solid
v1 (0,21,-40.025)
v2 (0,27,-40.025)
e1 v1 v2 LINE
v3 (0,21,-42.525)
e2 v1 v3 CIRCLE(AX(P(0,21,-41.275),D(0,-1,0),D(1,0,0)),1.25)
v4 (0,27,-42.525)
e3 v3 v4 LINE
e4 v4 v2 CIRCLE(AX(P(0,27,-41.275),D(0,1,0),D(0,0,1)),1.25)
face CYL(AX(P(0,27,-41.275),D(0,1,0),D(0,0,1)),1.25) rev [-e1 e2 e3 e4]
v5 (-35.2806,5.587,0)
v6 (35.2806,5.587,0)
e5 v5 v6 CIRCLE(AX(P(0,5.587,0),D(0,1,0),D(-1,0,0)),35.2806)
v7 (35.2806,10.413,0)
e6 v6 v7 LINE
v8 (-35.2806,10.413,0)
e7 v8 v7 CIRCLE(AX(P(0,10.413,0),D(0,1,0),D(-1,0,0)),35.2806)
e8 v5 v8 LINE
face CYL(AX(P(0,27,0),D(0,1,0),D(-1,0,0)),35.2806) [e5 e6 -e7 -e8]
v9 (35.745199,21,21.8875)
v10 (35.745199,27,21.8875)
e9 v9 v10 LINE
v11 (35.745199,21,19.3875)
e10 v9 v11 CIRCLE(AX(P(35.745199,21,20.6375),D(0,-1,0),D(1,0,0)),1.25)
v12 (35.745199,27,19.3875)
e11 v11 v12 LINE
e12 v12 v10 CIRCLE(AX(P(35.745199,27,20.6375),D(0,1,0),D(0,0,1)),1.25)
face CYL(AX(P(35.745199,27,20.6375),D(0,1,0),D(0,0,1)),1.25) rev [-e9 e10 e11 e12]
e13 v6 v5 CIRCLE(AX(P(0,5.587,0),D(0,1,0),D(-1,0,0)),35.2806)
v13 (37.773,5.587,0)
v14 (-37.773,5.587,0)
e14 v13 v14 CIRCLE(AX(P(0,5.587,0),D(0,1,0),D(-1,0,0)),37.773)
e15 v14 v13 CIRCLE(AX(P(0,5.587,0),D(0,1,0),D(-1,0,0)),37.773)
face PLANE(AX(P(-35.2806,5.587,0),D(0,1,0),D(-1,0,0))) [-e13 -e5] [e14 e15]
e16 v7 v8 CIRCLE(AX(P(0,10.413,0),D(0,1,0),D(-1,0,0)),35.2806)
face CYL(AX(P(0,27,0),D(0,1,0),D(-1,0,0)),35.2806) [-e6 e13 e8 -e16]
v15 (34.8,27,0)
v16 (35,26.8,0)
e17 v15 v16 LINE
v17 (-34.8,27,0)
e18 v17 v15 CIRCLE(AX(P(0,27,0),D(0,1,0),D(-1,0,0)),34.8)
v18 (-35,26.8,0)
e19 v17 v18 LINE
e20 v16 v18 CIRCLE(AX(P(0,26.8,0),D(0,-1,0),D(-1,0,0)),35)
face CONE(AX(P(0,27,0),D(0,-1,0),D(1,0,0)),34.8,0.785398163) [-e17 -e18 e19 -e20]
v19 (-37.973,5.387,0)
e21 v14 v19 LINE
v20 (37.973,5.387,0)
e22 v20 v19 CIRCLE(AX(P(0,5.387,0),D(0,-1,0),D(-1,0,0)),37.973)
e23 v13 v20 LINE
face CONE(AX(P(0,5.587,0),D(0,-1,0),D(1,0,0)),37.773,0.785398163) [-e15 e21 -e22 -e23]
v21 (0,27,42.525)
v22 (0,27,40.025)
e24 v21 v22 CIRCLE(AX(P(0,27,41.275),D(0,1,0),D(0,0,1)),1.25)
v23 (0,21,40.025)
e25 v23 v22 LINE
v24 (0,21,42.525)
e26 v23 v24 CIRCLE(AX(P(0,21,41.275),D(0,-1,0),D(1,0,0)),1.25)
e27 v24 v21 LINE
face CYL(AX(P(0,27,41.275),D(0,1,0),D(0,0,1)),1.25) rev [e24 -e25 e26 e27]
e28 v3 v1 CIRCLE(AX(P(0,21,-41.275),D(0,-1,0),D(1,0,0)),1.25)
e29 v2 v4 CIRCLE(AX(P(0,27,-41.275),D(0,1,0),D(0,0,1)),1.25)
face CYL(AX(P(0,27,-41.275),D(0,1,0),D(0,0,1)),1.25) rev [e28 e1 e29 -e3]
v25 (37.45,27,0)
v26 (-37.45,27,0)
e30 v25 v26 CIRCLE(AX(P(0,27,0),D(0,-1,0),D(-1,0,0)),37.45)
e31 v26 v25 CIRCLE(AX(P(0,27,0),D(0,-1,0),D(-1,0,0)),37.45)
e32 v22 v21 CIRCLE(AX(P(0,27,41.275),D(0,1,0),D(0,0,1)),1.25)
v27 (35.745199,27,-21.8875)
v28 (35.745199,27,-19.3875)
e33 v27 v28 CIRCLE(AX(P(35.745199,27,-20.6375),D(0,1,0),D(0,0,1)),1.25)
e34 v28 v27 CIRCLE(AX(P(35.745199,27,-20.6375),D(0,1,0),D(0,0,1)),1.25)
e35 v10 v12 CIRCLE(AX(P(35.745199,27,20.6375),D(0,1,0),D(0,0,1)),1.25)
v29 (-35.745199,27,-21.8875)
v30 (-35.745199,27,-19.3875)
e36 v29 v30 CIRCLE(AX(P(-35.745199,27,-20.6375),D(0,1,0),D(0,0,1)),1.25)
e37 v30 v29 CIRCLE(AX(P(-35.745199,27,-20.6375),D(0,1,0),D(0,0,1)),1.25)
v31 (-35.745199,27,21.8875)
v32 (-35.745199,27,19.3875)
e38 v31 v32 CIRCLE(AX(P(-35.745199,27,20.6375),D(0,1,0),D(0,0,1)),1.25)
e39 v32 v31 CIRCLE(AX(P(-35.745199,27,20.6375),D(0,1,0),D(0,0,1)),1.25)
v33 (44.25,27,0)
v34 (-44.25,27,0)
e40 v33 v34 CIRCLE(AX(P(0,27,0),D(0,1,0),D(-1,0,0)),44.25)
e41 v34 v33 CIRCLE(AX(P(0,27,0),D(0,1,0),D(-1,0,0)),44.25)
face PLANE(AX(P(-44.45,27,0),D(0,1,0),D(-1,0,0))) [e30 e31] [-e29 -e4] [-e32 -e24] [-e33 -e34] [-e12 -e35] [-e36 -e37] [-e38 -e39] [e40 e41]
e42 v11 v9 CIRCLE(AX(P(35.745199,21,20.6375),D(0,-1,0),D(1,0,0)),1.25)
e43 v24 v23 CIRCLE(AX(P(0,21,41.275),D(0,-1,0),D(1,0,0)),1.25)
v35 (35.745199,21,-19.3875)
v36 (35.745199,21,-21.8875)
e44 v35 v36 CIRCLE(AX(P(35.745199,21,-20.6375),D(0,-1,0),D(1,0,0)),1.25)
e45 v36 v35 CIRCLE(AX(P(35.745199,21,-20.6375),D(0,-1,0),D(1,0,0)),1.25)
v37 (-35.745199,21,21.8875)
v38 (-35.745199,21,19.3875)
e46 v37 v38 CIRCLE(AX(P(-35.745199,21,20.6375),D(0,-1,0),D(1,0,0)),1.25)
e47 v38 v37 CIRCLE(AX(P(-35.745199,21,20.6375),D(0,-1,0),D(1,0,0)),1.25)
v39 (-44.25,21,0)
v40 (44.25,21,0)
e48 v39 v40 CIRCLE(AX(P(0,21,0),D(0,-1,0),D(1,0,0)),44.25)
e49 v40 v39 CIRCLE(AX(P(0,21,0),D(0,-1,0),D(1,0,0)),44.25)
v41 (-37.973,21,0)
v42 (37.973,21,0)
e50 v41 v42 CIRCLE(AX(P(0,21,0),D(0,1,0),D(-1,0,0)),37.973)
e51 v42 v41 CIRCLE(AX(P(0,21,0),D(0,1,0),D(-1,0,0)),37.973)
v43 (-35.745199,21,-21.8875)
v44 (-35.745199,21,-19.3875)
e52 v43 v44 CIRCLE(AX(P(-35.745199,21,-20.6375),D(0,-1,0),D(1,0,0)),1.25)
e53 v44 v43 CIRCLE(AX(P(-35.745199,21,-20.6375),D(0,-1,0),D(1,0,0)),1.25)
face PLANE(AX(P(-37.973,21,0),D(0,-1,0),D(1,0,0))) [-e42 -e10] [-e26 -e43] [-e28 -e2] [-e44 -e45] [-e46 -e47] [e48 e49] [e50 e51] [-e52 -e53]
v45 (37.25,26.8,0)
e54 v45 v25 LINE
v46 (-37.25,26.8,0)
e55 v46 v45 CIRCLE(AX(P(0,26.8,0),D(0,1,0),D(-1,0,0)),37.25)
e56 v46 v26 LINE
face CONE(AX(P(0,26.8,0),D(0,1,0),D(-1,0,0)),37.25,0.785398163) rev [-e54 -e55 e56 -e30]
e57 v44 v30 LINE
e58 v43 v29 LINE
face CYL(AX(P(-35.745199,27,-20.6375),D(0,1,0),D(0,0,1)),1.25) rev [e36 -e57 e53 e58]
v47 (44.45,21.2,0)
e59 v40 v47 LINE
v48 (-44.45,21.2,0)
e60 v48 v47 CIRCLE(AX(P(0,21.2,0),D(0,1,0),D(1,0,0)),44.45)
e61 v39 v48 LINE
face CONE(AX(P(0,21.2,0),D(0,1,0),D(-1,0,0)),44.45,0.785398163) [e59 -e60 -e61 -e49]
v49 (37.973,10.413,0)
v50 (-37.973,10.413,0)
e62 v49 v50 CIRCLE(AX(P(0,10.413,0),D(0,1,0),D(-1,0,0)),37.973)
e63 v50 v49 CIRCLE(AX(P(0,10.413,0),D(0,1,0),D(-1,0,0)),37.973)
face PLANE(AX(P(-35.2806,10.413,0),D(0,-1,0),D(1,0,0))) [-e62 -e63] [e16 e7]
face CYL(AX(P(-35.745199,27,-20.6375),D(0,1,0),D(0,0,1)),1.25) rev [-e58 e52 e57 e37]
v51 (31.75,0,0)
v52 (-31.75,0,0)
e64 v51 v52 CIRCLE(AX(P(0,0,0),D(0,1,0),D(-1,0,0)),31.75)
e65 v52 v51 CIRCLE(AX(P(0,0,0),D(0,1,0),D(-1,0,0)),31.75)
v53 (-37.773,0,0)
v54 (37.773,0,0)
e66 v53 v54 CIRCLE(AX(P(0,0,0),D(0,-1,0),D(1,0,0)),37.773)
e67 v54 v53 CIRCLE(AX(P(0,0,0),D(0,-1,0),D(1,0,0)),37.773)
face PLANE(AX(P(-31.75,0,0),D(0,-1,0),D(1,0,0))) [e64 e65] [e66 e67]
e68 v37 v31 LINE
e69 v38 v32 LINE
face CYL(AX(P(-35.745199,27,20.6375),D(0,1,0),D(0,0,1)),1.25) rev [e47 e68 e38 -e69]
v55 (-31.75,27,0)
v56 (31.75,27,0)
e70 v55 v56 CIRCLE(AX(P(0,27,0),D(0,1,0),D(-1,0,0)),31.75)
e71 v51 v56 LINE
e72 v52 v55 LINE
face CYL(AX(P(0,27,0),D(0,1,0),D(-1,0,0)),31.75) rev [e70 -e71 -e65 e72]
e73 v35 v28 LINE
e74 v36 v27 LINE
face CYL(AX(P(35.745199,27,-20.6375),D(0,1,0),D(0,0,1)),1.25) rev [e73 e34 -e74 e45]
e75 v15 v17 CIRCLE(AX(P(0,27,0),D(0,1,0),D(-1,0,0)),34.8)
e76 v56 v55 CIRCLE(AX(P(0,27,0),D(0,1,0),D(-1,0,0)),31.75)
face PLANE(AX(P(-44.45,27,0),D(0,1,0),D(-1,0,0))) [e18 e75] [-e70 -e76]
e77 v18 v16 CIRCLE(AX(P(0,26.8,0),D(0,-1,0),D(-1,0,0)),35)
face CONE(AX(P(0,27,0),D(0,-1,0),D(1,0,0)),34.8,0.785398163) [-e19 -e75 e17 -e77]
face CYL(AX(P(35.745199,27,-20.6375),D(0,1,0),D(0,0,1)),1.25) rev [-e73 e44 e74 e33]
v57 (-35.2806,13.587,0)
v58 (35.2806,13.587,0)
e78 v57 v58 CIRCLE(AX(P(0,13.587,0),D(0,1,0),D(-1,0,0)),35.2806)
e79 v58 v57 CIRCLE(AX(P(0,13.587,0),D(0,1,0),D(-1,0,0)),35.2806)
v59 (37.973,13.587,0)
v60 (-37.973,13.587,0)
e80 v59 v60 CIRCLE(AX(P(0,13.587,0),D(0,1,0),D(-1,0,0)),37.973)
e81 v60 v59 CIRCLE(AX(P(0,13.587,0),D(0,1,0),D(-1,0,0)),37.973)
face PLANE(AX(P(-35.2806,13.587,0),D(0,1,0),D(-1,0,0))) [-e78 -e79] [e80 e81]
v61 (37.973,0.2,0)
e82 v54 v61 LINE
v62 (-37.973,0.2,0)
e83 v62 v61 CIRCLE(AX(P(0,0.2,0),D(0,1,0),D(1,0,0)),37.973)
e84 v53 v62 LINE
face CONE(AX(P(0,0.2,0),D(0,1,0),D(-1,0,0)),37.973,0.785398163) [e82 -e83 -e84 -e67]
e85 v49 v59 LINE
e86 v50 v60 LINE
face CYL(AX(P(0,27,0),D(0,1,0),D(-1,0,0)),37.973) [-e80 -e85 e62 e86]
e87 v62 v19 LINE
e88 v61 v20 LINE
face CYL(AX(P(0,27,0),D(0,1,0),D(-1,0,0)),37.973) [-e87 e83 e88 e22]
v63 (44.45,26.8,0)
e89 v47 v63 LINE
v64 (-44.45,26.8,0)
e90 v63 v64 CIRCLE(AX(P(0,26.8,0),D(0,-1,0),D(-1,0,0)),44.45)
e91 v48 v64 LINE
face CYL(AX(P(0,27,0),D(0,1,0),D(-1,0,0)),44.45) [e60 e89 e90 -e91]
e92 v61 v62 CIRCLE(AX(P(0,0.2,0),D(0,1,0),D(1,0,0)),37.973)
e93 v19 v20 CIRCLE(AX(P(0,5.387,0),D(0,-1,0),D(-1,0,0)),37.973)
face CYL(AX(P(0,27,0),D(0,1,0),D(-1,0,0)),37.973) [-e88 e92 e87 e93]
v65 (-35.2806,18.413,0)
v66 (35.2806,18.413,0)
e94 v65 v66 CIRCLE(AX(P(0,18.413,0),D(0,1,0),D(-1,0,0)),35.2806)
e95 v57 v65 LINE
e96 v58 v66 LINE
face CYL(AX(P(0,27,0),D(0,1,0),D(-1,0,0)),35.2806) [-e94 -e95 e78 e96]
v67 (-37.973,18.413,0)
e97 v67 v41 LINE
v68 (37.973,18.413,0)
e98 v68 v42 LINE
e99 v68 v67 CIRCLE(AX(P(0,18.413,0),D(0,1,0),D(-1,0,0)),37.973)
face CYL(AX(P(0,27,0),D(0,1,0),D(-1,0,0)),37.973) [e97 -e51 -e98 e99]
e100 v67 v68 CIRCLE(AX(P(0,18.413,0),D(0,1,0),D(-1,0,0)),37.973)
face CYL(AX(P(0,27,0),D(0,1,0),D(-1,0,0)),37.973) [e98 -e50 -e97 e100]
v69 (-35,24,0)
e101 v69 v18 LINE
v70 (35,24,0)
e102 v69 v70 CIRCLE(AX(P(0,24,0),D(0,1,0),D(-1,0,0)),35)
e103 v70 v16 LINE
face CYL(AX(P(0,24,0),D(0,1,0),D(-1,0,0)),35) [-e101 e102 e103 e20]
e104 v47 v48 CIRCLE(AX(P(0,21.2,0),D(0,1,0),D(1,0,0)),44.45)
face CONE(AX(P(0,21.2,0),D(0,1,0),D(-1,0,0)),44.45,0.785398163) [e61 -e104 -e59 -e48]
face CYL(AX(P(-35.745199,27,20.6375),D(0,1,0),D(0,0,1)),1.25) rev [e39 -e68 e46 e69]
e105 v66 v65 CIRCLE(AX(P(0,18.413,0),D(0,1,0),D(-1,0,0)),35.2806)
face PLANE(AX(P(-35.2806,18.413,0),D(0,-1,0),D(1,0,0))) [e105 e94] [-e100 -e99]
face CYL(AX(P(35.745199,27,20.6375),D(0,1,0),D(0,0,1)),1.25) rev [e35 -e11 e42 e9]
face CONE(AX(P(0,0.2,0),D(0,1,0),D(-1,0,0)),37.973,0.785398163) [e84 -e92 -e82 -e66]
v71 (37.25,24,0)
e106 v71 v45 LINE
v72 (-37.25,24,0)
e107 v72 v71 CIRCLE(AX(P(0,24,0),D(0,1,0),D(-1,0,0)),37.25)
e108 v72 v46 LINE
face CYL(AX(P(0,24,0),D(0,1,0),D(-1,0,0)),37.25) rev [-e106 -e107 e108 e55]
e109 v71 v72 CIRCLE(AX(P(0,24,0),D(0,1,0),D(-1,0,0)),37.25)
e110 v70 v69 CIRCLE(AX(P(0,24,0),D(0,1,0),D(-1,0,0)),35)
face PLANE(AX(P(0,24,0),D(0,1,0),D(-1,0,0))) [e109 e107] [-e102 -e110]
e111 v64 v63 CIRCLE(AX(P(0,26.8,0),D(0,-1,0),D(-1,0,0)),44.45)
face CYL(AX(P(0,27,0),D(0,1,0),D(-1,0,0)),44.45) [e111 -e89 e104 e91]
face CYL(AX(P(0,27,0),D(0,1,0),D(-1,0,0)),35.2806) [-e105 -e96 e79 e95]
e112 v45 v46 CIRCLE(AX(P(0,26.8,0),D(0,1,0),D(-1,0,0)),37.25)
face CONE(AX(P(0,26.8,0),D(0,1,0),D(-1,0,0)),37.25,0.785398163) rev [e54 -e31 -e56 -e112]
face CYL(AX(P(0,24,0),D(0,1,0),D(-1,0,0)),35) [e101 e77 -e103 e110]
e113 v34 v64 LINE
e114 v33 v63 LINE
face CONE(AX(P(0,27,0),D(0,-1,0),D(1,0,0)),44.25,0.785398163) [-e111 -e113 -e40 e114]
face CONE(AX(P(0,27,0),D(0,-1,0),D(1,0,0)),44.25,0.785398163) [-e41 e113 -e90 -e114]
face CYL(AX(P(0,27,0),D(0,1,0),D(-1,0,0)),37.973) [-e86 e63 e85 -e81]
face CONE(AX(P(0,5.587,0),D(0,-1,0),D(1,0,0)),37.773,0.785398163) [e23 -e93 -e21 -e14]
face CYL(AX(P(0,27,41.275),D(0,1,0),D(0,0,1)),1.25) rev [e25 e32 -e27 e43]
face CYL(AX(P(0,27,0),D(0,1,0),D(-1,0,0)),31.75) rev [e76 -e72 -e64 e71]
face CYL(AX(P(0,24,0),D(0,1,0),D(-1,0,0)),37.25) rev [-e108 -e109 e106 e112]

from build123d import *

# Parameters (mm, degrees)
CHAMFER_1_SIZE         = 0.2
HOLE_WIZARD_M3_1_D     = 2.5
HOLE_WIZARD_M3_1_DEPTH = 7.5
HOLE_WIZARD_M3_1_TIP   = 0.751075774
SKETCH_4_R             = 37.25
SKETCH_4_R_2           = 35
CUT_EXTRUDE_1_DEPTH    = 3
CHAMFER_2_SIZE         = 0.2


with BuildPart() as part:
    # 草图1 → 旋转1 (revolve)
    with BuildSketch(Plane.XY):
        Polygon((-31.75, 27), (-31.75, 0), (-37.973, 0), (-37.973, 5.587), (-35.2806, 5.587), (-35.2806, 10.413), (-37.973, 10.413), (-37.973, 13.587), (-35.2806, 13.587), (-35.2806, 18.413), (-37.973, 18.413), (-37.973, 21), (-44.45, 21), (-44.45, 27), align=None)
    revolve(axis=Axis((0, 27, 0), (0, -1, 0)))

    # 倒角1
    chamfer_1_edges = [part.edges().sort_by_distance(p)[0] for p in [
        (37.973, 5.587, 0),
        (37.973, 0, 0),
        (44.45, 27, 0),
        (44.45, 21, 0),
    ]]
    chamfer(chamfer_1_edges, length=CHAMFER_1_SIZE)

    # M3 螺纹孔1
    with Locations(Plane(origin=(0, 27, 0), x_dir=(1, 0, 0), z_dir=(0, 1, 0))):
        with Locations((-35.745198541, -20.6375), (-35.745198541, 20.6375), (0, 41.275), (35.745198541, 20.6375), (35.745198541, -20.6375), (0, -41.275)):
            Hole(HOLE_WIZARD_M3_1_D / 2, depth=HOLE_WIZARD_M3_1_DEPTH)
            with Locations((0, 0, -(HOLE_WIZARD_M3_1_DEPTH + HOLE_WIZARD_M3_1_TIP / 2))):  # 118° drill point
                Cone(0, HOLE_WIZARD_M3_1_D / 2, HOLE_WIZARD_M3_1_TIP, mode=Mode.SUBTRACT)

    # 草图4 → 切除-拉伸1 (cut)
    with BuildSketch(Plane(origin=(0, 27, 0), x_dir=(1, 0, 0), z_dir=(0, 1, 0))):
        with Locations(Location((0, 0, 0), (0, 0, 180))):
            Circle(SKETCH_4_R)
        with Locations(Location((0, 0, 0), (0, 0, 180))):
            Circle(SKETCH_4_R_2, mode=Mode.SUBTRACT)
    extrude(amount=-CUT_EXTRUDE_1_DEPTH, mode=Mode.SUBTRACT)

    # 倒角2
    chamfer_2_edges = [part.edges().sort_by_distance(p)[0] for p in [
        (37.25, 27, 0),
        (35, 27, 0),
    ]]
    chamfer(chamfer_2_edges, length=CHAMFER_2_SIZE)


solid = part.part
